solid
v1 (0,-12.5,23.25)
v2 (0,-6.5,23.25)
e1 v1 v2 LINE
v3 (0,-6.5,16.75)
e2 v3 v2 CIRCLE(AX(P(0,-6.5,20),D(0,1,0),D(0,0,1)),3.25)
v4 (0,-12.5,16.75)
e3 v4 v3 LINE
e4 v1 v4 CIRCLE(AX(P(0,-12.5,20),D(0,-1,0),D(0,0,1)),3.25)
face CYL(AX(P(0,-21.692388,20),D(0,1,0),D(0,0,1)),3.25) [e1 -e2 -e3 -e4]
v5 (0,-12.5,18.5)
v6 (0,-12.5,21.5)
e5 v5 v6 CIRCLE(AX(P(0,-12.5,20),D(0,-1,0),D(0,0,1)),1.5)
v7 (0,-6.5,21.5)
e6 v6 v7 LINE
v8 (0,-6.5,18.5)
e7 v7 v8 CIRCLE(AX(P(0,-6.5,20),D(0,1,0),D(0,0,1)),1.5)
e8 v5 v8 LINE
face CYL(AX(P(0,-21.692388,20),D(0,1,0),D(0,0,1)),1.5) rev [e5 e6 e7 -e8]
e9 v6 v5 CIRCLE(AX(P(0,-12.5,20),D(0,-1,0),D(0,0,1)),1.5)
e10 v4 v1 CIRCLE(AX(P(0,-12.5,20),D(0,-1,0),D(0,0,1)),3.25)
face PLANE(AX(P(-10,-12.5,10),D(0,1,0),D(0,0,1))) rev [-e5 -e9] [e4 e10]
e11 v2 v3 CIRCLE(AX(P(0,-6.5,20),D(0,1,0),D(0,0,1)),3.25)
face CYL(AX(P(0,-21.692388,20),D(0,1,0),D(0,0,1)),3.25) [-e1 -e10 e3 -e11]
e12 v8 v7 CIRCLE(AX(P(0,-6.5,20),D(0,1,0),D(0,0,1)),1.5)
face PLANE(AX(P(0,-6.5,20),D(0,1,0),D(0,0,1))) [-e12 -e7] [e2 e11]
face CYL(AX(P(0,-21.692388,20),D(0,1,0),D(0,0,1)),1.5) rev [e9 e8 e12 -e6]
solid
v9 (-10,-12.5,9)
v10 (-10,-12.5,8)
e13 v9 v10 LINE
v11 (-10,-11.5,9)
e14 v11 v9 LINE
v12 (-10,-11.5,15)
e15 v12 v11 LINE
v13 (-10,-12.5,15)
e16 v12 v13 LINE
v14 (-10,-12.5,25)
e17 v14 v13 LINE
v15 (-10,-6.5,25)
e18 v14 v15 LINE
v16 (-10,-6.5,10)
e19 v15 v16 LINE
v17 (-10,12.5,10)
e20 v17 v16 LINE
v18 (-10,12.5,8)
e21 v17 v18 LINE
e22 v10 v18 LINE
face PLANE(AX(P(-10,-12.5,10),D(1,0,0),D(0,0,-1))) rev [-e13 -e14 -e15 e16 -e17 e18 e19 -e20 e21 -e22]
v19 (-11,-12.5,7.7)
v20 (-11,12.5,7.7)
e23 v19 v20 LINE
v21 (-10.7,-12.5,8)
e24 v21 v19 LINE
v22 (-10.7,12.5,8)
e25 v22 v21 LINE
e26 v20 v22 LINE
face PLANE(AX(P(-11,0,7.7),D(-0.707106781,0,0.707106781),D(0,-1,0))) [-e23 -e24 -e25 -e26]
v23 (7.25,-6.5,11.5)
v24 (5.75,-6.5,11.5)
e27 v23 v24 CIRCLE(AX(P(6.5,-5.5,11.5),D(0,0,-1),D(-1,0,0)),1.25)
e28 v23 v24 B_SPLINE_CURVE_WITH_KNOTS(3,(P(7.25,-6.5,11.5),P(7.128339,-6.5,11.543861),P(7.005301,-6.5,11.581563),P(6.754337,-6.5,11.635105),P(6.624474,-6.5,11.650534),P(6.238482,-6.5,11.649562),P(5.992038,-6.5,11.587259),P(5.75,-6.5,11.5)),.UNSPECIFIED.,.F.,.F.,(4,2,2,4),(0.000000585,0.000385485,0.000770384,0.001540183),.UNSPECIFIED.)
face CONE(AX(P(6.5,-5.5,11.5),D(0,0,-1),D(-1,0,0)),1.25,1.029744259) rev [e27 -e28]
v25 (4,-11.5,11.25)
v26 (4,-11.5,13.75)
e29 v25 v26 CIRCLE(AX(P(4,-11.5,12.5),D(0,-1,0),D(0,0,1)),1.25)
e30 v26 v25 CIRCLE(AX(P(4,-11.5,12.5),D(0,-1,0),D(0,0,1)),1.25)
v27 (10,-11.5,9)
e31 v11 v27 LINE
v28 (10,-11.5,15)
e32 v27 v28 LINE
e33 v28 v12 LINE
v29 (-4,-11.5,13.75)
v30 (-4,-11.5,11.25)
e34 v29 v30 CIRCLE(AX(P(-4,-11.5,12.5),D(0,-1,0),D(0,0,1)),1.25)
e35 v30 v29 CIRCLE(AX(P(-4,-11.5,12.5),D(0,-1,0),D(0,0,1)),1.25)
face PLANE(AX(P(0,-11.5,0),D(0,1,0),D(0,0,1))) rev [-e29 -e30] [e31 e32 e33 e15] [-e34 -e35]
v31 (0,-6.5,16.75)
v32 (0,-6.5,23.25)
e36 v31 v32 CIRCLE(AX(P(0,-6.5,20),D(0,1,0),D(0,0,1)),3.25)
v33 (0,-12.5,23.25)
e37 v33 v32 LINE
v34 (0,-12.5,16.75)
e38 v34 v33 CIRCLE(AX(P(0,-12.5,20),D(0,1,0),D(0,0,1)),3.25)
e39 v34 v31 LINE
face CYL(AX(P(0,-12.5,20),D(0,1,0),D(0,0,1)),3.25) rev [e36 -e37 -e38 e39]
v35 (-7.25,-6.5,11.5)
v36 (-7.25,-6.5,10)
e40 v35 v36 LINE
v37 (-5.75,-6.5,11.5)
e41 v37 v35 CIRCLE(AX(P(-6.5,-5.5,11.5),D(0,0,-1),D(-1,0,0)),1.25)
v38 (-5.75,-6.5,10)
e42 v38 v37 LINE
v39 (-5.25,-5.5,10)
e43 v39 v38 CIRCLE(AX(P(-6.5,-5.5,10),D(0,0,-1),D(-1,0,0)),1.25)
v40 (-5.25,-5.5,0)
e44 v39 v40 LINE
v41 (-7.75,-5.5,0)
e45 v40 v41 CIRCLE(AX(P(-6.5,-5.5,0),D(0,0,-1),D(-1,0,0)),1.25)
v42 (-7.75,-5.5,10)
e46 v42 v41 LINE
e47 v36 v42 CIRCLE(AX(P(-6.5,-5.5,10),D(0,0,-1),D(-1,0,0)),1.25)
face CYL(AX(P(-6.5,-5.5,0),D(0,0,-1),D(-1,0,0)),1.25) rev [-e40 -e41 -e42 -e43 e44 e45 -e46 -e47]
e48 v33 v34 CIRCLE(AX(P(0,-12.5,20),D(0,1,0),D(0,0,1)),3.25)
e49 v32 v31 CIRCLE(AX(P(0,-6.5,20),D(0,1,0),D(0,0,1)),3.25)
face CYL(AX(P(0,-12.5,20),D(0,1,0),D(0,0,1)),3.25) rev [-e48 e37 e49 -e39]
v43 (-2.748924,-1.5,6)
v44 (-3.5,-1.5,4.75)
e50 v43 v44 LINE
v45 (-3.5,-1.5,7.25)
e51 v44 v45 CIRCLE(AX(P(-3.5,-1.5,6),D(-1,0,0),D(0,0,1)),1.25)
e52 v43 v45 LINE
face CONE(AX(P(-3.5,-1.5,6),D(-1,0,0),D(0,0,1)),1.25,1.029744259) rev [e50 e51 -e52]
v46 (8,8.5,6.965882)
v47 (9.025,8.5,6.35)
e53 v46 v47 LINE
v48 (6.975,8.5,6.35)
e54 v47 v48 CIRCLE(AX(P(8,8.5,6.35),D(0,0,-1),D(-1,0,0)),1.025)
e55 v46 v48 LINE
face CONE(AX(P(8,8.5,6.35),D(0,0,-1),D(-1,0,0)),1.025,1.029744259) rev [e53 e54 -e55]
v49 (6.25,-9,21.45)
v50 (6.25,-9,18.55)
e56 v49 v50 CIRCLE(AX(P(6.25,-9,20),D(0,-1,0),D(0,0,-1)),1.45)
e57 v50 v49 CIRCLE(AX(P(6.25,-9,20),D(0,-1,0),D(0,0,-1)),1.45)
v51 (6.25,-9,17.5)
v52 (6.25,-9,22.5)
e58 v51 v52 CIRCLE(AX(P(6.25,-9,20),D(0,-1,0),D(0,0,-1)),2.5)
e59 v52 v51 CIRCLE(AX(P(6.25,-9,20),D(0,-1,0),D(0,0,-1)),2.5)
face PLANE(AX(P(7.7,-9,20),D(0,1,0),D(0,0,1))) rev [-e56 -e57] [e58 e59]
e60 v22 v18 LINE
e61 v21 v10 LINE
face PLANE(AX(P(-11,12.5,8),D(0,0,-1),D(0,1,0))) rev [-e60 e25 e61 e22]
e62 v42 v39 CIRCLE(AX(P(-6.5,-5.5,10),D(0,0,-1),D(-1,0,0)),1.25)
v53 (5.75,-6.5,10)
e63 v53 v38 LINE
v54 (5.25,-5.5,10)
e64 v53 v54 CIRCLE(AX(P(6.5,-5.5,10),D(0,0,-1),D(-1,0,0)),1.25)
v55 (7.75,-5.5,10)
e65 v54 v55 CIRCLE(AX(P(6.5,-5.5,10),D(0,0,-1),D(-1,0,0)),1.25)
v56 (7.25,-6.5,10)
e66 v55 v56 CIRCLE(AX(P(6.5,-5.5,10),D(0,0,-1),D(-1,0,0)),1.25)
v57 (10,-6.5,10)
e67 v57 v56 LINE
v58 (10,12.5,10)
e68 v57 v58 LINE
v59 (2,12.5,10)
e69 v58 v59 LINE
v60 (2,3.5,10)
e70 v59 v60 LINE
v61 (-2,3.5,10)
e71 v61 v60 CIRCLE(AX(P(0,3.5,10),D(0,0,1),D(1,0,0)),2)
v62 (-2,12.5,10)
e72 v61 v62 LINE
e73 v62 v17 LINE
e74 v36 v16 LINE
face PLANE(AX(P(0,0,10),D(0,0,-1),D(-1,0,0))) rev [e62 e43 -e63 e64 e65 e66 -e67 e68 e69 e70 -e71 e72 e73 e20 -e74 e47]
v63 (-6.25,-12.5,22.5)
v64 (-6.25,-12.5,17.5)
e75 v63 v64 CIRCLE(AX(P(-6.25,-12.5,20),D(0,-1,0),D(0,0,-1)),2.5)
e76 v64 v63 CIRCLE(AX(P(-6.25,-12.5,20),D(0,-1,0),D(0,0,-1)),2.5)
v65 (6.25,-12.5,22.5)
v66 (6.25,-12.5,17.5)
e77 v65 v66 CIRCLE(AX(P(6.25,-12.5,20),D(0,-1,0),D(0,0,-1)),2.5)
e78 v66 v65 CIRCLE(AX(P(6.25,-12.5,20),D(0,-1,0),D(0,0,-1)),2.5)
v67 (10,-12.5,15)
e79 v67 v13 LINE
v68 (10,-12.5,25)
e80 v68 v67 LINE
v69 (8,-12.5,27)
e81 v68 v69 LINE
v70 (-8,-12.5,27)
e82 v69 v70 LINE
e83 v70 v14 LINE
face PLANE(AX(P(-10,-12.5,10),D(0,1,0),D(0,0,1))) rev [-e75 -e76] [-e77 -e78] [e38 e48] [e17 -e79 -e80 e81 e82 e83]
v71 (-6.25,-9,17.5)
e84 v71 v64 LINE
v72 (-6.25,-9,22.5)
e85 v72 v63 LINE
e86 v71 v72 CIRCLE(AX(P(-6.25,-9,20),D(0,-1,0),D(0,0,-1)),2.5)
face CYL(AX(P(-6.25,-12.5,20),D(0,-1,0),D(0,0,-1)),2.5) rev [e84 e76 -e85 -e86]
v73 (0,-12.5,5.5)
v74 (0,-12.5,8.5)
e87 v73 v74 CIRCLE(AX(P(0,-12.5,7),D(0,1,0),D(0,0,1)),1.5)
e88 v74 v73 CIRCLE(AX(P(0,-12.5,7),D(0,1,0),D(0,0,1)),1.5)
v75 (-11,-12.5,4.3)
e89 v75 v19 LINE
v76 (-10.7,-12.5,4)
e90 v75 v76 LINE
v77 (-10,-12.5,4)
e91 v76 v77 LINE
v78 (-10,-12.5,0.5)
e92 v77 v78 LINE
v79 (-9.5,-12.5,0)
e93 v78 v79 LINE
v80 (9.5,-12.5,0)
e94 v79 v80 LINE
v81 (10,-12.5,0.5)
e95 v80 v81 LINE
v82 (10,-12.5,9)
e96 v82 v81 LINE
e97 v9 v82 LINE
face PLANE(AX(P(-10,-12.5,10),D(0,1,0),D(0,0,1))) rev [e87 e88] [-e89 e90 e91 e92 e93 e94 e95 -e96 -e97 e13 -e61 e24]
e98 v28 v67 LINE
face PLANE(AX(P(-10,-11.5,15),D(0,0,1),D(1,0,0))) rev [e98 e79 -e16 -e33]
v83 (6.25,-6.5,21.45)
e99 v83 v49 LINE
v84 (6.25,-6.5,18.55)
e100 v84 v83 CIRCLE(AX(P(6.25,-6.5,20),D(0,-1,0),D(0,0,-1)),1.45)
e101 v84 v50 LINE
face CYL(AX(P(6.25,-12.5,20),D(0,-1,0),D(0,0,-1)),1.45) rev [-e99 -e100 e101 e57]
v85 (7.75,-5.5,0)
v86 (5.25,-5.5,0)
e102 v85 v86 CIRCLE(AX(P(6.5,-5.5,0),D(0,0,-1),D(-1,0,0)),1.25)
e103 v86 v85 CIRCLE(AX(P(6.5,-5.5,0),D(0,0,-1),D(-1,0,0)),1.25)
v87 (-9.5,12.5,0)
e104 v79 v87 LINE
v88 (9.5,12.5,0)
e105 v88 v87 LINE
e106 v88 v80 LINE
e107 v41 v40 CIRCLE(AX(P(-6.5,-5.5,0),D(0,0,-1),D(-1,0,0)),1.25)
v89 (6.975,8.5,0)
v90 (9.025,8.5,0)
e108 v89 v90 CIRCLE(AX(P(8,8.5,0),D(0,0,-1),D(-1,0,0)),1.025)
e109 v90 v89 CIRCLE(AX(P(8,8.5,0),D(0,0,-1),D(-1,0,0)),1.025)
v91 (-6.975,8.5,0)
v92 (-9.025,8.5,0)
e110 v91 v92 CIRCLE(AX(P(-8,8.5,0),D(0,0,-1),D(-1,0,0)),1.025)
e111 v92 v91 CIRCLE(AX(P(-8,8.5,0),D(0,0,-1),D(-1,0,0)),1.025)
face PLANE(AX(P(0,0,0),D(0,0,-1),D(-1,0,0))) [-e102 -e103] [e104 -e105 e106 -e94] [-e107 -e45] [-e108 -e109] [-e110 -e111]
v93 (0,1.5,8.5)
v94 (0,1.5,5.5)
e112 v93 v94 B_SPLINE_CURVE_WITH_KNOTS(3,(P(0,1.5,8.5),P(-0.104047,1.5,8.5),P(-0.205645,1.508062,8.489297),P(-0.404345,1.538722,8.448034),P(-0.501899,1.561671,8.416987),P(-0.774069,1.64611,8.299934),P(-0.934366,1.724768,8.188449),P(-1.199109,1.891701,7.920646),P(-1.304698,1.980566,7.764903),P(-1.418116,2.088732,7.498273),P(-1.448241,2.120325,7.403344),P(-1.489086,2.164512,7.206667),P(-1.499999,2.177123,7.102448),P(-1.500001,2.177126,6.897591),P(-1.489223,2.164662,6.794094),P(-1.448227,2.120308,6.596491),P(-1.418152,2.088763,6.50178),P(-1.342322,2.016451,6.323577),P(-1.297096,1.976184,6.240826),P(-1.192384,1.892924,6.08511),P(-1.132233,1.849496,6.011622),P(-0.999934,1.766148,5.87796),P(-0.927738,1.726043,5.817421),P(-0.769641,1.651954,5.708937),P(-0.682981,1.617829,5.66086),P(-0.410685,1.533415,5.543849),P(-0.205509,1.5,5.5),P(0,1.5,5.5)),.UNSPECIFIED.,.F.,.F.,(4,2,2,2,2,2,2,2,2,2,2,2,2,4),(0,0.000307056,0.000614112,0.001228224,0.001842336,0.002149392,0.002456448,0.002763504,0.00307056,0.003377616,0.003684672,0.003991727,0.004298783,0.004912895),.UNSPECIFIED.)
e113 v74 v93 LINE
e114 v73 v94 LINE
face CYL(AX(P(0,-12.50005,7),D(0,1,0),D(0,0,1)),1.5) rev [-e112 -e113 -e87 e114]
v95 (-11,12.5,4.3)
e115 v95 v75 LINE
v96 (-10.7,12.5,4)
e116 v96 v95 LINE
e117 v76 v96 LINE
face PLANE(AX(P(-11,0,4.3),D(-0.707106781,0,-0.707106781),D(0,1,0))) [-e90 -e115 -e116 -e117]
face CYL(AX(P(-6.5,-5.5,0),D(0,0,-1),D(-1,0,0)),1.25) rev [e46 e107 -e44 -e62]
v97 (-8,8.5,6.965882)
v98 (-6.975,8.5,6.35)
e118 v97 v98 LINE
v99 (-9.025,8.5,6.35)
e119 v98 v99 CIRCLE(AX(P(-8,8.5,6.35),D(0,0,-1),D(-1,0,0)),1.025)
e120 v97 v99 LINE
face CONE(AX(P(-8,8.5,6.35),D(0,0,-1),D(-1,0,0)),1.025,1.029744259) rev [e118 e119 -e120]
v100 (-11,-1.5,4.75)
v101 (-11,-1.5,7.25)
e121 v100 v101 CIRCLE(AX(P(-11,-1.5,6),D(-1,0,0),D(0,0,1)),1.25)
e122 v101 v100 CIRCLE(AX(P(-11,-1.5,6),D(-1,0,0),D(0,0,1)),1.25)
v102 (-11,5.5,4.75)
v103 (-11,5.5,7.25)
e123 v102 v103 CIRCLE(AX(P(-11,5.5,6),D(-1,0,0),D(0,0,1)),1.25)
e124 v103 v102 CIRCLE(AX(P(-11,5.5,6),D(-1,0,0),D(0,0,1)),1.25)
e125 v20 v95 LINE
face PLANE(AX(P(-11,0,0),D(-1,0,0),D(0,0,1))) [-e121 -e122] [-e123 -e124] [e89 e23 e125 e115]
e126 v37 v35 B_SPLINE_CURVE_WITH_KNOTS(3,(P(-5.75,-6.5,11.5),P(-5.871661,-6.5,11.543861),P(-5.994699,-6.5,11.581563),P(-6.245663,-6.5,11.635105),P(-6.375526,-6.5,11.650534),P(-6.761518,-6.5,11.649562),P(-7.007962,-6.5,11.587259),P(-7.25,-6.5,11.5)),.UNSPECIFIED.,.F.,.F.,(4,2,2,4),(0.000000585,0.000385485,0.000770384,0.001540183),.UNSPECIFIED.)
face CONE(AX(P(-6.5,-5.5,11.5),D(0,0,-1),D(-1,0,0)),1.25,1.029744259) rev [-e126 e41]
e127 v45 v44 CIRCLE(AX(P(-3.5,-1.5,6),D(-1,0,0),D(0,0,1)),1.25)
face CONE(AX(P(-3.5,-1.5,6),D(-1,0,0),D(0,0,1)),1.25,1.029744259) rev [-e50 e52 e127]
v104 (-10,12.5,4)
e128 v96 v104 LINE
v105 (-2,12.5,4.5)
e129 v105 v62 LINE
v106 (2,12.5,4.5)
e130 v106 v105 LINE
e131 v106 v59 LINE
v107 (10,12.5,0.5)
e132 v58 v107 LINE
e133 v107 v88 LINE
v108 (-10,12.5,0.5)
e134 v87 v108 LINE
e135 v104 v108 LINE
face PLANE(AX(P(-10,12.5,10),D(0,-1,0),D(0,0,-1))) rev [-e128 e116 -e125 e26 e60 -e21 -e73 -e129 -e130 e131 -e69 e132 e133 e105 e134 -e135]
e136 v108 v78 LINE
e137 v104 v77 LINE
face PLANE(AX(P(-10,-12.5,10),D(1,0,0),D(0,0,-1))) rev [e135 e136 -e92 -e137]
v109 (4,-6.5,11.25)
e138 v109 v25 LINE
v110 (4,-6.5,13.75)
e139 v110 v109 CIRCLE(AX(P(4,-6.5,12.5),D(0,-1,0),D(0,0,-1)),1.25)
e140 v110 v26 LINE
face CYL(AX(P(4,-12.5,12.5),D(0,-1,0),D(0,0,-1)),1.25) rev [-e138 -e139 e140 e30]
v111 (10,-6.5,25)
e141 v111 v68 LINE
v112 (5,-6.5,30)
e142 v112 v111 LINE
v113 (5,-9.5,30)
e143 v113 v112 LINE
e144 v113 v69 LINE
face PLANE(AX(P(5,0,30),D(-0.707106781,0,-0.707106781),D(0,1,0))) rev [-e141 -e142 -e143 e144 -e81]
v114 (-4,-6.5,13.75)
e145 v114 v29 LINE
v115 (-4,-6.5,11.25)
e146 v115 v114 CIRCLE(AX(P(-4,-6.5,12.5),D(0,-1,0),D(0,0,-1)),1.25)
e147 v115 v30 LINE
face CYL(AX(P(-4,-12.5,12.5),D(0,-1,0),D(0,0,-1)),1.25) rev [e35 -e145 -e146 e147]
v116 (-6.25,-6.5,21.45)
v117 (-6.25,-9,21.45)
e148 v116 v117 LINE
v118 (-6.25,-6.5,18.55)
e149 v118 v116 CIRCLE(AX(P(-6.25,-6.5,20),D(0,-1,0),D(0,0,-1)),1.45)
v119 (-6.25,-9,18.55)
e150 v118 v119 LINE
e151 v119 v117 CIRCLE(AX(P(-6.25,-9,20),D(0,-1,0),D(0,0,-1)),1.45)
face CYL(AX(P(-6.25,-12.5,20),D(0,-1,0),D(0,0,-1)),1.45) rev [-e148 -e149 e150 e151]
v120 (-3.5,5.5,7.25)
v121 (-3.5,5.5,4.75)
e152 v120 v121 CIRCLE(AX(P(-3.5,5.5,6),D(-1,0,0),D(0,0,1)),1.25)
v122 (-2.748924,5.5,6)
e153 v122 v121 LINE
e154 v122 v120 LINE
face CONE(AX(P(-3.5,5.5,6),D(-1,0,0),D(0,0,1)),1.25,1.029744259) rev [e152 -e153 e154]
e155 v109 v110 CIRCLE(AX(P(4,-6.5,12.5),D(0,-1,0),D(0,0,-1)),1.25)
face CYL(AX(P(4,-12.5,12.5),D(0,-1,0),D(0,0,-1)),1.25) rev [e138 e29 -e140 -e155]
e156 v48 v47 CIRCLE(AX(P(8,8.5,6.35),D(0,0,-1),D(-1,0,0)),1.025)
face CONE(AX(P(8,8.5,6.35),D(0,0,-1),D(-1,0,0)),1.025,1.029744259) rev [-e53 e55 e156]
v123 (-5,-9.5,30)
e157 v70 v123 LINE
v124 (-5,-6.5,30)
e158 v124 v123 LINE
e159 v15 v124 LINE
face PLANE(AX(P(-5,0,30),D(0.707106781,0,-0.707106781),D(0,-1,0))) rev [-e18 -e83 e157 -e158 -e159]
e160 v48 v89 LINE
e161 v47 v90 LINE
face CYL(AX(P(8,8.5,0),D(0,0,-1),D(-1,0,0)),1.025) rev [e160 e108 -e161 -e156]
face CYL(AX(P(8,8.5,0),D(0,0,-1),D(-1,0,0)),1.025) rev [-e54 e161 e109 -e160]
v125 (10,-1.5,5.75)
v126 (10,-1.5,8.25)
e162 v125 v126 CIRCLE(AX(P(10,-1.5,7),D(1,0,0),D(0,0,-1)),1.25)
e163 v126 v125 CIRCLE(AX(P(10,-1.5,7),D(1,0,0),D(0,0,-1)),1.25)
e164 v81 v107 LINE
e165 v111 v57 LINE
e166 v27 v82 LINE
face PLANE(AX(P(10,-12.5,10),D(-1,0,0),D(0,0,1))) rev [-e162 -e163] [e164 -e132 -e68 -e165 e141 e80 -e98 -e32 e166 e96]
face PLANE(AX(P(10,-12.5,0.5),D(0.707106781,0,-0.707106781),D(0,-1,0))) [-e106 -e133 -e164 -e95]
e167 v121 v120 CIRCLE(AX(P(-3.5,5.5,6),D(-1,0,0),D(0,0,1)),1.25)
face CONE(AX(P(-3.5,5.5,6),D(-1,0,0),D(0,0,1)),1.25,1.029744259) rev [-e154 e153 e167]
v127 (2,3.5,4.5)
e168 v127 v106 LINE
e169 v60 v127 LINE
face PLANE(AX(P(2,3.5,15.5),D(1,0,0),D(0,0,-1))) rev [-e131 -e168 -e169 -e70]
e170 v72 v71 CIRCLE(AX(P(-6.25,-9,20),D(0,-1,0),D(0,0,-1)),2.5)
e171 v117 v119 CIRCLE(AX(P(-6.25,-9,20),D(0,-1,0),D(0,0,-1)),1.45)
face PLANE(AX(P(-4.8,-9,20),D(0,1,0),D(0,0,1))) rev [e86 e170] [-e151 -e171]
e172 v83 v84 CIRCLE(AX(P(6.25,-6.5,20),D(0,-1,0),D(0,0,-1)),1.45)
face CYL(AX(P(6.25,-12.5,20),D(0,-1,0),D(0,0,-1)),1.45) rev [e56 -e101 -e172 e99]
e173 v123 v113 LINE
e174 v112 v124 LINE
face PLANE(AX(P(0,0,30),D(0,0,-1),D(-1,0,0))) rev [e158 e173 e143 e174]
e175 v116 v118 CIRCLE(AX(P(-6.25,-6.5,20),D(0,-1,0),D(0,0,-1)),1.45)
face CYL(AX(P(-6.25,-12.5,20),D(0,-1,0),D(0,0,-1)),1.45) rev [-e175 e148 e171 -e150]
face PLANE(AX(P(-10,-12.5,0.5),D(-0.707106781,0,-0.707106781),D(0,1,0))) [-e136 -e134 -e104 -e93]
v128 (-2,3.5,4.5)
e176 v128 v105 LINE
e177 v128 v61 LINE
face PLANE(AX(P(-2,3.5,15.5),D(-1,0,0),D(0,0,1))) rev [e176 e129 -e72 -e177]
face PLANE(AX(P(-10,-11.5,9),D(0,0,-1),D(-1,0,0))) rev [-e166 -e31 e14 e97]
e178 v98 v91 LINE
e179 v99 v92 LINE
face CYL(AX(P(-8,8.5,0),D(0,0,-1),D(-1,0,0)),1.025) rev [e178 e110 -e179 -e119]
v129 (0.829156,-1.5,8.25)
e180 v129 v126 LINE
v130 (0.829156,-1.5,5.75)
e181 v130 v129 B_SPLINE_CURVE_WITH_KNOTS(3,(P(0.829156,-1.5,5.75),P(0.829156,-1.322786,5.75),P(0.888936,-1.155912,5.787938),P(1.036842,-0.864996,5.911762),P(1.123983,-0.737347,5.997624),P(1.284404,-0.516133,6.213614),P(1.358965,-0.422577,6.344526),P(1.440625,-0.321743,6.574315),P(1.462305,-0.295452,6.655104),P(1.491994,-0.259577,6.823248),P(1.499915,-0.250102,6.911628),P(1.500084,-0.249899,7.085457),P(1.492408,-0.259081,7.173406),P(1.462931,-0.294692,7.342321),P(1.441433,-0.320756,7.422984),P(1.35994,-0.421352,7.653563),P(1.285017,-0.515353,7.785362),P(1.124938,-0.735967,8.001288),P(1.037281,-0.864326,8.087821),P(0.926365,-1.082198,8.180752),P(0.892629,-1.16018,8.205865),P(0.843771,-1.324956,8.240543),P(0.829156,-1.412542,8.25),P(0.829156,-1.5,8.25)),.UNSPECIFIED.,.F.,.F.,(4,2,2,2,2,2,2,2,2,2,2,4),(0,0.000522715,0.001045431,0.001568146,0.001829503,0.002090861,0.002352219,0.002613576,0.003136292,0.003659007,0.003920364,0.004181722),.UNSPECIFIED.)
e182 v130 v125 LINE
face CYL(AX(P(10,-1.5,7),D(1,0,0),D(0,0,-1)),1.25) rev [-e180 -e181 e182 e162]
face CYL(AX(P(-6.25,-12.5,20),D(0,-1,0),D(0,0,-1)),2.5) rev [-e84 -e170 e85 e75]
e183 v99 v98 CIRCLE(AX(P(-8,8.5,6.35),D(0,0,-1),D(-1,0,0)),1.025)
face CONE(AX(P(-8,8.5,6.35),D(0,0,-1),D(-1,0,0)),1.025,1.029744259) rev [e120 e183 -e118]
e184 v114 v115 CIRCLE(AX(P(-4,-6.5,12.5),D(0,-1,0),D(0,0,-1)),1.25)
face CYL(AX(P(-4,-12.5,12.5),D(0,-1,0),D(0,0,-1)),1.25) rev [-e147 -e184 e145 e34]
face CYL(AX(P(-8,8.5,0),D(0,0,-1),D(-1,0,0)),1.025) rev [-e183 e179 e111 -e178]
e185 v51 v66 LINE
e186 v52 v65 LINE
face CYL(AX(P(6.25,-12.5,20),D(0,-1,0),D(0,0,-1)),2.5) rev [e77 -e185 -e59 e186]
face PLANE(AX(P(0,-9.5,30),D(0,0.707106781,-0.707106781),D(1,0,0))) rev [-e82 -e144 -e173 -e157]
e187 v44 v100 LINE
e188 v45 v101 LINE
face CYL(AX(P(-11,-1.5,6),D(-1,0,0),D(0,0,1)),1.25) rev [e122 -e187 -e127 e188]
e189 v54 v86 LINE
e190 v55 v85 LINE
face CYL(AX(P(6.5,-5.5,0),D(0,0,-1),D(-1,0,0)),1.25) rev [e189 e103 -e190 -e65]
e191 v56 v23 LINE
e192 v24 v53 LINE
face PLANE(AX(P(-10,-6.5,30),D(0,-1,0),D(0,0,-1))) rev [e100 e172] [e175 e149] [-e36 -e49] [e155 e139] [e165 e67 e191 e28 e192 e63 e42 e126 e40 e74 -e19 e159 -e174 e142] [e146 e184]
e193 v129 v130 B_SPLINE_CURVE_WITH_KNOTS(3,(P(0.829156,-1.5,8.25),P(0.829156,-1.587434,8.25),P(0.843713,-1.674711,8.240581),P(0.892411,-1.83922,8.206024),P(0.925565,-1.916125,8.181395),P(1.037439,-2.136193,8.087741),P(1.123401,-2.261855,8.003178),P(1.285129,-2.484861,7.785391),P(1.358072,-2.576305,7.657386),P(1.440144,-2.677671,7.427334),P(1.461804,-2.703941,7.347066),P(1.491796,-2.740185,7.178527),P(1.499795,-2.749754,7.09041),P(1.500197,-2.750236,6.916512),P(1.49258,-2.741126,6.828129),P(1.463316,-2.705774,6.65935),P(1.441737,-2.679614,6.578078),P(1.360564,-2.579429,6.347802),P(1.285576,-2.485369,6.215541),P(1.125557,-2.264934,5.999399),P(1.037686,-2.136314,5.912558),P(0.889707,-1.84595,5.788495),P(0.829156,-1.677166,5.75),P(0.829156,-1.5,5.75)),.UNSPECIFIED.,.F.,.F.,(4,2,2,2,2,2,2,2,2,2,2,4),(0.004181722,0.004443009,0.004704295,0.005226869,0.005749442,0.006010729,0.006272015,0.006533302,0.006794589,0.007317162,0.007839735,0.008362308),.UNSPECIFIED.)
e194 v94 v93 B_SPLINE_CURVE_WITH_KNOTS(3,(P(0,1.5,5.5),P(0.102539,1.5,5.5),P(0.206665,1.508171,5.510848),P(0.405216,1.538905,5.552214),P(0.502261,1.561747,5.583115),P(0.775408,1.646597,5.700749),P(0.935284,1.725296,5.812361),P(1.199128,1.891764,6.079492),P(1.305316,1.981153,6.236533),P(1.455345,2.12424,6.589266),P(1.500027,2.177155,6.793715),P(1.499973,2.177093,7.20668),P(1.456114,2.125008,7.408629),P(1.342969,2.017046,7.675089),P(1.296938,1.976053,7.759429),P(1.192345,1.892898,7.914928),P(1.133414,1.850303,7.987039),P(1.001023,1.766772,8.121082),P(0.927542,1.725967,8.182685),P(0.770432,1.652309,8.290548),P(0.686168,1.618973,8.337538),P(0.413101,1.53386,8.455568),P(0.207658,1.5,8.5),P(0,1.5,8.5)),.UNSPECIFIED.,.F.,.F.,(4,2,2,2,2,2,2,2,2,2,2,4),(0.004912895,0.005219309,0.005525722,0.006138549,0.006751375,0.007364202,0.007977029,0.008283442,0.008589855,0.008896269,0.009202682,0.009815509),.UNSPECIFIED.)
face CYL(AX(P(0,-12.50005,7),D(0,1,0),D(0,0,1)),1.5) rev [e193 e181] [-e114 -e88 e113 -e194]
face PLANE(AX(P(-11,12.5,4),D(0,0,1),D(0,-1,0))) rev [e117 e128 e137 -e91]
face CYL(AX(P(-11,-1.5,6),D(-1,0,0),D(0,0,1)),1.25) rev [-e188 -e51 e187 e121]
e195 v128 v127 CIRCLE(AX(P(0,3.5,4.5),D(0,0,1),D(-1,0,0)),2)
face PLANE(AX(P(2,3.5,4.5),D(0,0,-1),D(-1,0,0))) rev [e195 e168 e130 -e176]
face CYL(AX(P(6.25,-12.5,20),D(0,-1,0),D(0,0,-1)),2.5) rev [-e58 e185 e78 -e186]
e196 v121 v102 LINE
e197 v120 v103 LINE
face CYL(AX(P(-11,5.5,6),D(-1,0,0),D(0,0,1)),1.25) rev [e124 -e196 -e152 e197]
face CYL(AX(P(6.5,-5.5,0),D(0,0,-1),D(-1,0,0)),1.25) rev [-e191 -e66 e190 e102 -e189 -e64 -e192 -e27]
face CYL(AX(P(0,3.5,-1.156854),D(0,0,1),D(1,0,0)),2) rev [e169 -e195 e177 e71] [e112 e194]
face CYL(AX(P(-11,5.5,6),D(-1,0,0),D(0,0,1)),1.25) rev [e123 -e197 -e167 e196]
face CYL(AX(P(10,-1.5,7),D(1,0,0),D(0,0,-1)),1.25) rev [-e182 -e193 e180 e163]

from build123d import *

# Parameters (mm, degrees)
SKETCH1_W                                   = 20
SKETCH1_H                                   = 25
BOSS_EXTRUDE1_DEPTH                         = 10
SKETCH2_W                                   = 20
SKETCH2_H                                   = 6
BOSS_EXTRUDE2_DEPTH                         = 20
SKETCH3_W                                   = 4
SKETCH3_H                                   = 11
CUT_EXTRUDE1_DEPTH                          = 9
SKETCH4_R                                   = 3.25
CUT_EXTRUDE2_DEPTH                          = 37.891733491
SKETCH5_R                                   = 3.25
SKETCH5_R_2                                 = 1.5
BOSS_EXTRUDE3_DEPTH                         = 6
HOLE_SIZE_PER_SOCKET_HEAD_CAP_SCREW_2_COUNT = 2
HOLE_SIZE_PER_SOCKET_HEAD_CAP_SCREW_2_PITCH = 12.5
SKETCH9_W                                   = 4
SKETCH9_H                                   = 25
BOSS_EXTRUDE4_DEPTH                         = 1
M3_TAPPED_HOLE1_AT_2_COUNT                  = 2
M3_TAPPED_HOLE1_AT_2_PITCH                  = 7
CHAMFER1_SIZE                               = 0.3
SKETCH13_R                                  = 2
CUT_EXTRUDE4_DEPTH                          = 5.5
M2_5_TAPPED_HOLE1_AT_2_COUNT                = 2
M2_5_TAPPED_HOLE1_AT_2_PITCH                = 16
CHAMFER2_SIZE                               = 5
CHAMFER3_SIZE                               = 0.5
M3_TAPPED_HOLE2_AT_2_COUNT                  = 2
M3_TAPPED_HOLE2_AT_2_PITCH                  = 13
M3_TAPPED_HOLE3_AT_2_COUNT                  = 2
M3_TAPPED_HOLE3_AT_2_PITCH                  = 8
SKETCH20_W                                  = 20
SKETCH20_H                                  = 6
CUT_EXTRUDE5_DEPTH                          = 1
CHAMFER4_SIZE                               = 3
SKETCH21_R                                  = 1.5
CUT_EXTRUDE9_DEPTH                          = 41.57092555


with BuildPart() as part:
    # Sketch1 → Boss-Extrude1 (new body)
    with BuildSketch(Plane.XY):
        Rectangle(SKETCH1_W, SKETCH1_H)
    extrude(amount=BOSS_EXTRUDE1_DEPTH)

    # Sketch2 → Boss-Extrude2 (add)
    with BuildSketch(Plane.XY.offset(10)):
        with Locations((0, -9.5)):
            Rectangle(SKETCH2_W, SKETCH2_H)
    extrude(amount=BOSS_EXTRUDE2_DEPTH)

    # Sketch3 → Cut-Extrude1 (cut)
    with BuildSketch(Plane(origin=(0, 12.5, 0), x_dir=(1, 0, 0), z_dir=(0, 1, 0))):
        with Locations((0, -10)):
            Rectangle(SKETCH3_W, SKETCH3_H)
    extrude(amount=-CUT_EXTRUDE1_DEPTH, mode=Mode.SUBTRACT)

    # Sketch4 → Cut-Extrude2 (cut, through all)
    with BuildSketch(Plane(origin=(0, -6.5, 0), x_dir=(1, 0, 0), z_dir=(0, 1, 0))):
        with Locations(Location((0, -20, 0), (0, 0, 270))):
            Circle(SKETCH4_R)
    extrude(amount=-CUT_EXTRUDE2_DEPTH, mode=Mode.SUBTRACT)

    # Sketch6 → Hole size per socket head cap screw type 1 (revolve, cut)
    with BuildSketch(Plane(origin=(6.25, -12.5, 20), x_dir=(0, 0, -1), z_dir=(1, 0, 0))):
        Polygon((0, 0), (0, 25.000025), (1.45, 25.000025), (1.45, 3.5), (2.5, 3.5), (2.5, 0), align=None)
    hole_size_per_socket_head_cap_screw_type = revolve(axis=Axis((6.25, -18.85, 20), (0, 1, 0)), mode=Mode.SUBTRACT)

    # Hole size per socket head cap screw  2: Hole size per socket head cap screw type 1 ×2
    with Locations(*[(-i * HOLE_SIZE_PER_SOCKET_HEAD_CAP_SCREW_2_PITCH, 0, 0) for i in range(1, HOLE_SIZE_PER_SOCKET_HEAD_CAP_SCREW_2_COUNT)]):
        add(hole_size_per_socket_head_cap_screw_type, mode=Mode.SUBTRACT)

    # Sketch9 → Boss-Extrude4 (add)
    with BuildSketch(Plane.ZY.offset(10)):
        with Locations((6, 0)):
            Rectangle(SKETCH9_W, SKETCH9_H)
    extrude(amount=BOSS_EXTRUDE4_DEPTH)

    # Sketch10 → M3 Tapped Hole1 (revolve, cut)
    with BuildSketch(Plane(origin=(-11, 5.5, 6), x_dir=(0, 0, 1), z_dir=(0, 1, 0))):
        Polygon((0, 0), (0, 8.251075774), (1.25, 7.5), (1.25, 0), align=None)
    m3_tapped_hole1 = revolve(axis=Axis((-17.35, 5.5, 6), (1, 0, 0)), mode=Mode.SUBTRACT)

    # M3 Tapped Hole1 at 2: M3 Tapped Hole1 ×2
    with Locations(*[(0, -i * M3_TAPPED_HOLE1_AT_2_PITCH, 0) for i in range(1, M3_TAPPED_HOLE1_AT_2_COUNT)]):
        add(m3_tapped_hole1, mode=Mode.SUBTRACT)

    # Chamfer1
    chamfer1_edges = [part.edges().sort_by_distance(p)[0] for p in [
        (-11, 0, 8),
        (-11, 0, 4),
    ]]
    chamfer(chamfer1_edges, length=CHAMFER1_SIZE)

    # Sketch13 → Cut-Extrude4 (cut)
    with BuildSketch(Plane.XY.offset(10)):
        with Locations((0, 3.5)):
            Circle(SKETCH13_R)
    extrude(amount=-CUT_EXTRUDE4_DEPTH, mode=Mode.SUBTRACT)

    # Sketch14 → M2.5 Tapped Hole1 (revolve, cut)
    with BuildSketch(Plane(origin=(8, 8.5, 0), x_dir=(0, 1, 0), z_dir=(1, 0, 0))):
        Polygon((0, 0), (0, 6.965882135), (1.025, 6.35), (1.025, 0), align=None)
    m2_5_tapped_hole1 = revolve(axis=Axis((8, 8.5, -6.35), (0, 0, 1)), mode=Mode.SUBTRACT)

    # M2.5 Tapped Hole1 at 2: M2.5 Tapped Hole1 ×2
    with Locations(*[(-i * M2_5_TAPPED_HOLE1_AT_2_PITCH, 0, 0) for i in range(1, M2_5_TAPPED_HOLE1_AT_2_COUNT)]):
        add(m2_5_tapped_hole1, mode=Mode.SUBTRACT)

    # Chamfer2
    chamfer2_edges = [part.edges().sort_by_distance(p)[0] for p in [
        (-10, -9.5, 30),
        (10, -9.5, 30),
    ]]
    chamfer(chamfer2_edges, length=CHAMFER2_SIZE)

    # Chamfer3
    chamfer3_edges = [part.edges().sort_by_distance(p)[0] for p in [
        (-10, 0, 0),
        (10, 0, 0),
    ]]
    chamfer(chamfer3_edges, length=CHAMFER3_SIZE)

    # Sketch16 → M3 Tapped Hole2 (revolve, cut)
    with BuildSketch(Plane(origin=(6.5, -5.5, 0), x_dir=(0, 1, 0), z_dir=(1, 0, 0))):
        Polygon((0, 0), (0, 12.251075774), (1.25, 11.5), (1.25, 0), align=None)
    m3_tapped_hole2 = revolve(axis=Axis((6.5, -5.5, -6.35), (0, 0, 1)), mode=Mode.SUBTRACT)

    # M3 Tapped Hole2 at 2: M3 Tapped Hole2 ×2
    with Locations(*[(-i * M3_TAPPED_HOLE2_AT_2_PITCH, 0, 0) for i in range(1, M3_TAPPED_HOLE2_AT_2_COUNT)]):
        add(m3_tapped_hole2, mode=Mode.SUBTRACT)

    # Sketch18 → M3 Tapped Hole3 (revolve, cut)
    with BuildSketch(Plane(origin=(-4, -12.5, 12.5), x_dir=(0, 0, -1), z_dir=(1, 0, 0))):
        Polygon((0, 0), (0, 8.251075774), (1.25, 7.5), (1.25, 0), align=None)
    m3_tapped_hole3 = revolve(axis=Axis((-4, -18.85, 12.5), (0, 1, 0)), mode=Mode.SUBTRACT)

    # M3 Tapped Hole3 at 2: M3 Tapped Hole3 ×2
    with Locations(*[(i * M3_TAPPED_HOLE3_AT_2_PITCH, 0, 0) for i in range(1, M3_TAPPED_HOLE3_AT_2_COUNT)]):
        add(m3_tapped_hole3, mode=Mode.SUBTRACT)

    # Sketch20 → Cut-Extrude5 (cut)
    with BuildSketch(Plane.XZ.offset(12.5)):
        with Locations((0, 12)):
            Rectangle(SKETCH20_W, SKETCH20_H)
    extrude(amount=-CUT_EXTRUDE5_DEPTH, mode=Mode.SUBTRACT)

    # Chamfer4
    chamfer4_edges = [part.edges().sort_by_distance(p)[0] for p in [
        (0, -12.5, 30),
    ]]
    chamfer(chamfer4_edges, length=CHAMFER4_SIZE)

    # Sketch21 → Cut-Extrude9 (cut, through all)
    with BuildSketch(Plane(origin=(0, 12.5, 0), x_dir=(1, 0, 0), z_dir=(0, 1, 0))):
        with Locations(Location((0, -7, 0), (0, 0, 270))):
            Circle(SKETCH21_R)
    extrude(amount=-CUT_EXTRUDE9_DEPTH, mode=Mode.SUBTRACT)

    # Sketch22 → M3 Tapped Hole4 (revolve, cut)
    with BuildSketch(Plane(origin=(10, -1.5, 7), x_dir=(0, 0, -1), z_dir=(0, 1, 0))):
        Polygon((0, 0), (0, 11.251075774), (1.25, 10.5), (1.25, 0), align=None)
    revolve(axis=Axis((16.35, -1.5, 7), (-1, 0, 0)), mode=Mode.SUBTRACT)


with BuildPart() as body_2:
    # Sketch5 → Boss-Extrude3 (new body)
    with BuildSketch(Plane(origin=(0, -6.5, 0), x_dir=(1, 0, 0), z_dir=(0, 1, 0))):
        with Locations(Location((0, -20, 0), (0, 0, 270))):
            Circle(SKETCH5_R)
        with Locations(Location((0, -20, 0), (0, 0, 270))):
            Circle(SKETCH5_R_2, mode=Mode.SUBTRACT)
    extrude(amount=-BOSS_EXTRUDE3_DEPTH)


solid = Compound([part.part, body_2.part])
